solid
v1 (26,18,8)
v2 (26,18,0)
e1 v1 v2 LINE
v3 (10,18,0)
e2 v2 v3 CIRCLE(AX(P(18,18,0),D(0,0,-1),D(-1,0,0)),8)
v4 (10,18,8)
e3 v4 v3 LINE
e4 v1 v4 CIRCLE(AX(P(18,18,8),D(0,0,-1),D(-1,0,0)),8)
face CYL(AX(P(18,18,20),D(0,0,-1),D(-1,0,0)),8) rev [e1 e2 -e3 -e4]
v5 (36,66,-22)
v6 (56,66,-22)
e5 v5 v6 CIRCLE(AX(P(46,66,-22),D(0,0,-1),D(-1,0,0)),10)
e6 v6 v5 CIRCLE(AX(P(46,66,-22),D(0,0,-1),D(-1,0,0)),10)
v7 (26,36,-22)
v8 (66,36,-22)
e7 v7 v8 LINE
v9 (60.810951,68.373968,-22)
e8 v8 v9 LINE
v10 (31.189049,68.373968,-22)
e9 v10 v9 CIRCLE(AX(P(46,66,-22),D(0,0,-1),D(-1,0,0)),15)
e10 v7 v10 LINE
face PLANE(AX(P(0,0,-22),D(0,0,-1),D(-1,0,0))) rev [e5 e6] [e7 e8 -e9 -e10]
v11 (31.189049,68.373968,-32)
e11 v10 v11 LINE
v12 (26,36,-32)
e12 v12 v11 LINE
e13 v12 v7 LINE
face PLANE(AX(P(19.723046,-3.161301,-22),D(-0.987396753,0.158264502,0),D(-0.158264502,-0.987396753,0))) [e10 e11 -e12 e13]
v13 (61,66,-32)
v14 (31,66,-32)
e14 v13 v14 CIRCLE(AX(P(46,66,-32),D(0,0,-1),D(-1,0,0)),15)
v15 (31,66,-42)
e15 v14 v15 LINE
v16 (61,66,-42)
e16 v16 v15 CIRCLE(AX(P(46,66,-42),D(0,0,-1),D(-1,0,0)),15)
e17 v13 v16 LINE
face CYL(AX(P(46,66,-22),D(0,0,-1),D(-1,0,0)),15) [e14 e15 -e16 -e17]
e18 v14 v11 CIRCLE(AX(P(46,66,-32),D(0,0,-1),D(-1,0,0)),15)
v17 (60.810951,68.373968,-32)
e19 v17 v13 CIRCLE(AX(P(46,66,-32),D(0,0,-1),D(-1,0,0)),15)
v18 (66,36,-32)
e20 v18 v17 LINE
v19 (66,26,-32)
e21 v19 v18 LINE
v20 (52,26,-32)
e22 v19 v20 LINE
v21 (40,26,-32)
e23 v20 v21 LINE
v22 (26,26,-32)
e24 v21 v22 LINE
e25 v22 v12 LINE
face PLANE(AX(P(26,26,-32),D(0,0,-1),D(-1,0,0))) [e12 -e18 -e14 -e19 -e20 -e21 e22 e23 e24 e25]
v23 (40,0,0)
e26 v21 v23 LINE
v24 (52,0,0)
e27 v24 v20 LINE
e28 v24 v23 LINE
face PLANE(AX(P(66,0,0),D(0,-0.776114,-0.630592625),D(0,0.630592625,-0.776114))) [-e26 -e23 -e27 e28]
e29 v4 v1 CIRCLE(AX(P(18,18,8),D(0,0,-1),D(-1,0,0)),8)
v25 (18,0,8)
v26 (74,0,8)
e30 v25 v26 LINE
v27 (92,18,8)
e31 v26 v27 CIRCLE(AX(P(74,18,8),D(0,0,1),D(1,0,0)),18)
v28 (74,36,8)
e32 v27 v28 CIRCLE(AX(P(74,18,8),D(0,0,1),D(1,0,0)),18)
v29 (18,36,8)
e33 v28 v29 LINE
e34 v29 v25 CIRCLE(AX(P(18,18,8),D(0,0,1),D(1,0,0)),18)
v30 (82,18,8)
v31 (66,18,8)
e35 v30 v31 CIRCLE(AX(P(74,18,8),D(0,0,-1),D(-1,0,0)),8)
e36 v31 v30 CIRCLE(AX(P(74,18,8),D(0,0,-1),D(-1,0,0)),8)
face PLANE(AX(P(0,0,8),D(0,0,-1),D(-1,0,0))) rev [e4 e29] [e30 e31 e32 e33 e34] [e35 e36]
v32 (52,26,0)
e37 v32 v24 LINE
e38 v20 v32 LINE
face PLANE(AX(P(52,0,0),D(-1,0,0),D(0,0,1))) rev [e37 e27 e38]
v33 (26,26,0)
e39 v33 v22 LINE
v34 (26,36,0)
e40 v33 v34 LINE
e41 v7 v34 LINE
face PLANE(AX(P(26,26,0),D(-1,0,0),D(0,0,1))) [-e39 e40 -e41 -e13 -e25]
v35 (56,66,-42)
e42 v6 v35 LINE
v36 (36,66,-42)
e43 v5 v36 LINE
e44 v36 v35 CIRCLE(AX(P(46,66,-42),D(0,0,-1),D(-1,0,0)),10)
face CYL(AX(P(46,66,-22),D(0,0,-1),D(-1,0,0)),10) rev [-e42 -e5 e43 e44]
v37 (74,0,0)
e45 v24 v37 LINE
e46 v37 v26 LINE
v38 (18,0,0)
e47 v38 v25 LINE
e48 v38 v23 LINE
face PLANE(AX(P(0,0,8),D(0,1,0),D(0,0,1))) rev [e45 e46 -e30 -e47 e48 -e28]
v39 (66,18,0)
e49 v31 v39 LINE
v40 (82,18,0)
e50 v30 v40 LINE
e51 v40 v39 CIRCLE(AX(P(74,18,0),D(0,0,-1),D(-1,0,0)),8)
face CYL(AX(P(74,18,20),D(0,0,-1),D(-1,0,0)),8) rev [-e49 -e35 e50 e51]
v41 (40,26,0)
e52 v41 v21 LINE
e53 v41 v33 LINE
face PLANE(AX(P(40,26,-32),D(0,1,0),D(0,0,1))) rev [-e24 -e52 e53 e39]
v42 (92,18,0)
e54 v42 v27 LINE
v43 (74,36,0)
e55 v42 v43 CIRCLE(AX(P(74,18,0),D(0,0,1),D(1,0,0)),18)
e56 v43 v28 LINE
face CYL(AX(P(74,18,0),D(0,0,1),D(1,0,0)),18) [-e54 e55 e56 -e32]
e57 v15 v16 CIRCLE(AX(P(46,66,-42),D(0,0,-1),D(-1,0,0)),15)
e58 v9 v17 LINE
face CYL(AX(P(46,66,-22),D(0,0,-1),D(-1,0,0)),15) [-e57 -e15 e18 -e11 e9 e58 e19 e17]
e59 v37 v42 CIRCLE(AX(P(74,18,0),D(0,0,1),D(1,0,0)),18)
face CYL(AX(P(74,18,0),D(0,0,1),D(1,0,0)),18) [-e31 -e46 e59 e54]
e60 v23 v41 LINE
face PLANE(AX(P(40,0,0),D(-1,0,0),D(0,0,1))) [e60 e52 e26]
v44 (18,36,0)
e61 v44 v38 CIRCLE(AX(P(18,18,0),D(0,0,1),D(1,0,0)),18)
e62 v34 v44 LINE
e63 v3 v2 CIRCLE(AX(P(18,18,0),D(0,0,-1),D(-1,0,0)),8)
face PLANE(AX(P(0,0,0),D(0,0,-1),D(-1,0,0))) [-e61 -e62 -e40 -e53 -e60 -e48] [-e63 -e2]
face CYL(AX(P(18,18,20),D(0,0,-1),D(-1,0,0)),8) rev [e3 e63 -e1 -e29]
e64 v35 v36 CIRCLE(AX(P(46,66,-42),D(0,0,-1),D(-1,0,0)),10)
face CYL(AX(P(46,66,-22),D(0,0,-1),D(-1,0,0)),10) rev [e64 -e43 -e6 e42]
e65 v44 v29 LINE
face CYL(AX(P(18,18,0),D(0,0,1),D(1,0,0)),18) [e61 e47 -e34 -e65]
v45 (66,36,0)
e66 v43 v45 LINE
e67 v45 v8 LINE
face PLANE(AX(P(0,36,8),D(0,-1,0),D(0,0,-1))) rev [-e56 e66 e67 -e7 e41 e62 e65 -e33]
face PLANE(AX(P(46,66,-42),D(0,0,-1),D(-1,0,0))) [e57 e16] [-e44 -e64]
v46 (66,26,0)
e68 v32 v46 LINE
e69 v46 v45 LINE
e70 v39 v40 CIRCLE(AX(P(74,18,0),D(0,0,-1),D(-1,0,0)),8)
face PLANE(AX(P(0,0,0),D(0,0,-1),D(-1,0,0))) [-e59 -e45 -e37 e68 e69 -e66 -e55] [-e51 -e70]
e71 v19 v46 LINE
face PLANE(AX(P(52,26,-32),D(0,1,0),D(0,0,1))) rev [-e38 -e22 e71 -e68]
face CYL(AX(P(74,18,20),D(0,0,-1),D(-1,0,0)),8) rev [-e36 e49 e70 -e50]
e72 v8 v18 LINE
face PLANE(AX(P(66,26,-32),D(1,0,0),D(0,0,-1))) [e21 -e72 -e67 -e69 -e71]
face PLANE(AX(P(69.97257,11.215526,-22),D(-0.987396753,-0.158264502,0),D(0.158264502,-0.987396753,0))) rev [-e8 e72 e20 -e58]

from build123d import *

# Parameters (mm, degrees)
BASE_PLATE_SKETCH_W        = 92
BASE_PLATE_SKETCH_H        = 36
BASE_PLATE_DEPTH           = 8
ROUNDED_ENDS_R18_DEPTH     = 8
UPRIGHT_LEG_DEPTH          = 10
LUG_HEAD_DEPTH             = 10
RAISED_START               = 10
ROUND_BOSS_SKETCH_R        = 15
RAISED_ROUND_BOSS_30_DEPTH = 10
BOSS_BORE_SKETCH_R         = 10
BOSS_BORE_20_DEPTH         = 20
MOUNTING_HOLES_SKETCH_R    = 8
MOUNTING_HOLES_2X_16_DEPTH = 20
RIB_DEPTH                  = 40
RIB_TRIM_CUT_1_DEPTH       = 14
RIB_TRIM_CUT_2_DEPTH       = 14


with BuildPart() as part:
    # Base Plate Sketch → Base Plate (new body)
    with BuildSketch(Plane.XY):
        with Locations((46, 18)):
            Rectangle(BASE_PLATE_SKETCH_W, BASE_PLATE_SKETCH_H)
    extrude(amount=BASE_PLATE_DEPTH)

    # Rounded Ends Sketch → Rounded Ends R18 (cut)
    with BuildSketch(Plane.XY.offset(8)):
        with BuildLine():
            Line((18, 36), (0, 36))
            Line((0, 36), (0, 18))
            ThreePointArc((0, 18), (5.272077939, 30.727922061), (18, 36))
        make_face()
        with BuildLine():
            ThreePointArc((18, 0), (5.272077939, 5.272077939), (0, 18))
            Line((0, 18), (0, 0))
            Line((0, 0), (18, 0))
        make_face()
        with BuildLine():
            Line((92, 0), (92, 18))
            ThreePointArc((92, 18), (86.727922061, 5.272077939), (74, 0))
            Line((74, 0), (92, 0))
        make_face()
        with BuildLine():
            Line((92, 36), (74, 36))
            ThreePointArc((74, 36), (86.727922061, 30.727922061), (92, 18))
            Line((92, 18), (92, 36))
        make_face()
    extrude(amount=-ROUNDED_ENDS_R18_DEPTH, mode=Mode.SUBTRACT)

    # Upright Leg Sketch → Upright Leg (add)
    with BuildSketch(Plane(origin=(0, 36, 0), x_dir=(1, 0, 0), z_dir=(0, 1, 0))):
        Polygon((46, 0), (26, 0), (26, 32), (66, 32), (66, 0), align=None)
    extrude(amount=-UPRIGHT_LEG_DEPTH)

    # Lug Head Sketch → Lug Head (add)
    with BuildSketch(Plane(origin=(0, 0, -32), x_dir=(-1, 0, 0), z_dir=(0, 0, -1))):
        with BuildLine():
            Line((-66, 36), (-26, 36))
            Line((-26, 36), (-31.189048708, 68.373967528))
            ThreePointArc((-31.189048708, 68.373967528), (-46, 81), (-60.810951292, 68.373967528))
            Line((-60.810951292, 68.373967528), (-66, 36))
        make_face()
    extrude(amount=-LUG_HEAD_DEPTH)

    # Round Boss Sketch → Raised Round Boss Ø30 (add)
    with BuildSketch(Plane(origin=(0, 0, -32), x_dir=(-1, 0, 0), z_dir=(0, 0, -1)).offset(RAISED_START)):
        with Locations((-46, 66)):
            Circle(ROUND_BOSS_SKETCH_R)
    extrude(amount=-RAISED_ROUND_BOSS_30_DEPTH)

    # Boss Bore Sketch → Boss Bore Ø20 (cut)
    with BuildSketch(Plane(origin=(0, 0, -42), x_dir=(-1, 0, 0), z_dir=(0, 0, -1))):
        with Locations((-46, 66)):
            Circle(BOSS_BORE_SKETCH_R)
    extrude(amount=-BOSS_BORE_20_DEPTH, mode=Mode.SUBTRACT)

    # Mounting Holes Sketch → Mounting Holes 2xØ16 (cut)
    with BuildSketch(Plane(origin=(0, 0, 0), x_dir=(-1, 0, 0), z_dir=(0, 0, -1))):
        with Locations((-74, 18)):
            Circle(MOUNTING_HOLES_SKETCH_R)
        with Locations((-18, 18)):
            Circle(MOUNTING_HOLES_SKETCH_R)
    extrude(amount=-MOUNTING_HOLES_2X_16_DEPTH, mode=Mode.SUBTRACT)

    # Rib Sketch → Rib (add)
    with BuildSketch(Plane.ZY.offset(-26)):
        Polygon((-32, 26), (0, 26), (0, 0), align=None)
    extrude(amount=-RIB_DEPTH)

    # Rib Trim Sketch 1 → Rib Trim Cut 1 (cut)
    with BuildSketch(Plane.ZY.offset(-26)):
        Polygon((-32, 26), (0, 26), (0, 0), align=None)
    extrude(amount=-RIB_TRIM_CUT_1_DEPTH, mode=Mode.SUBTRACT)

    # Rib Trim Sketch 2 → Rib Trim Cut 2 (cut)
    with BuildSketch(Plane(origin=(66, 0, 0), x_dir=(0, 0, -1), z_dir=(1, 0, 0))):
        Polygon((32, 26), (0, 26), (0, 0), align=None)
    extrude(amount=-RIB_TRIM_CUT_2_DEPTH, mode=Mode.SUBTRACT)


solid = part.part
